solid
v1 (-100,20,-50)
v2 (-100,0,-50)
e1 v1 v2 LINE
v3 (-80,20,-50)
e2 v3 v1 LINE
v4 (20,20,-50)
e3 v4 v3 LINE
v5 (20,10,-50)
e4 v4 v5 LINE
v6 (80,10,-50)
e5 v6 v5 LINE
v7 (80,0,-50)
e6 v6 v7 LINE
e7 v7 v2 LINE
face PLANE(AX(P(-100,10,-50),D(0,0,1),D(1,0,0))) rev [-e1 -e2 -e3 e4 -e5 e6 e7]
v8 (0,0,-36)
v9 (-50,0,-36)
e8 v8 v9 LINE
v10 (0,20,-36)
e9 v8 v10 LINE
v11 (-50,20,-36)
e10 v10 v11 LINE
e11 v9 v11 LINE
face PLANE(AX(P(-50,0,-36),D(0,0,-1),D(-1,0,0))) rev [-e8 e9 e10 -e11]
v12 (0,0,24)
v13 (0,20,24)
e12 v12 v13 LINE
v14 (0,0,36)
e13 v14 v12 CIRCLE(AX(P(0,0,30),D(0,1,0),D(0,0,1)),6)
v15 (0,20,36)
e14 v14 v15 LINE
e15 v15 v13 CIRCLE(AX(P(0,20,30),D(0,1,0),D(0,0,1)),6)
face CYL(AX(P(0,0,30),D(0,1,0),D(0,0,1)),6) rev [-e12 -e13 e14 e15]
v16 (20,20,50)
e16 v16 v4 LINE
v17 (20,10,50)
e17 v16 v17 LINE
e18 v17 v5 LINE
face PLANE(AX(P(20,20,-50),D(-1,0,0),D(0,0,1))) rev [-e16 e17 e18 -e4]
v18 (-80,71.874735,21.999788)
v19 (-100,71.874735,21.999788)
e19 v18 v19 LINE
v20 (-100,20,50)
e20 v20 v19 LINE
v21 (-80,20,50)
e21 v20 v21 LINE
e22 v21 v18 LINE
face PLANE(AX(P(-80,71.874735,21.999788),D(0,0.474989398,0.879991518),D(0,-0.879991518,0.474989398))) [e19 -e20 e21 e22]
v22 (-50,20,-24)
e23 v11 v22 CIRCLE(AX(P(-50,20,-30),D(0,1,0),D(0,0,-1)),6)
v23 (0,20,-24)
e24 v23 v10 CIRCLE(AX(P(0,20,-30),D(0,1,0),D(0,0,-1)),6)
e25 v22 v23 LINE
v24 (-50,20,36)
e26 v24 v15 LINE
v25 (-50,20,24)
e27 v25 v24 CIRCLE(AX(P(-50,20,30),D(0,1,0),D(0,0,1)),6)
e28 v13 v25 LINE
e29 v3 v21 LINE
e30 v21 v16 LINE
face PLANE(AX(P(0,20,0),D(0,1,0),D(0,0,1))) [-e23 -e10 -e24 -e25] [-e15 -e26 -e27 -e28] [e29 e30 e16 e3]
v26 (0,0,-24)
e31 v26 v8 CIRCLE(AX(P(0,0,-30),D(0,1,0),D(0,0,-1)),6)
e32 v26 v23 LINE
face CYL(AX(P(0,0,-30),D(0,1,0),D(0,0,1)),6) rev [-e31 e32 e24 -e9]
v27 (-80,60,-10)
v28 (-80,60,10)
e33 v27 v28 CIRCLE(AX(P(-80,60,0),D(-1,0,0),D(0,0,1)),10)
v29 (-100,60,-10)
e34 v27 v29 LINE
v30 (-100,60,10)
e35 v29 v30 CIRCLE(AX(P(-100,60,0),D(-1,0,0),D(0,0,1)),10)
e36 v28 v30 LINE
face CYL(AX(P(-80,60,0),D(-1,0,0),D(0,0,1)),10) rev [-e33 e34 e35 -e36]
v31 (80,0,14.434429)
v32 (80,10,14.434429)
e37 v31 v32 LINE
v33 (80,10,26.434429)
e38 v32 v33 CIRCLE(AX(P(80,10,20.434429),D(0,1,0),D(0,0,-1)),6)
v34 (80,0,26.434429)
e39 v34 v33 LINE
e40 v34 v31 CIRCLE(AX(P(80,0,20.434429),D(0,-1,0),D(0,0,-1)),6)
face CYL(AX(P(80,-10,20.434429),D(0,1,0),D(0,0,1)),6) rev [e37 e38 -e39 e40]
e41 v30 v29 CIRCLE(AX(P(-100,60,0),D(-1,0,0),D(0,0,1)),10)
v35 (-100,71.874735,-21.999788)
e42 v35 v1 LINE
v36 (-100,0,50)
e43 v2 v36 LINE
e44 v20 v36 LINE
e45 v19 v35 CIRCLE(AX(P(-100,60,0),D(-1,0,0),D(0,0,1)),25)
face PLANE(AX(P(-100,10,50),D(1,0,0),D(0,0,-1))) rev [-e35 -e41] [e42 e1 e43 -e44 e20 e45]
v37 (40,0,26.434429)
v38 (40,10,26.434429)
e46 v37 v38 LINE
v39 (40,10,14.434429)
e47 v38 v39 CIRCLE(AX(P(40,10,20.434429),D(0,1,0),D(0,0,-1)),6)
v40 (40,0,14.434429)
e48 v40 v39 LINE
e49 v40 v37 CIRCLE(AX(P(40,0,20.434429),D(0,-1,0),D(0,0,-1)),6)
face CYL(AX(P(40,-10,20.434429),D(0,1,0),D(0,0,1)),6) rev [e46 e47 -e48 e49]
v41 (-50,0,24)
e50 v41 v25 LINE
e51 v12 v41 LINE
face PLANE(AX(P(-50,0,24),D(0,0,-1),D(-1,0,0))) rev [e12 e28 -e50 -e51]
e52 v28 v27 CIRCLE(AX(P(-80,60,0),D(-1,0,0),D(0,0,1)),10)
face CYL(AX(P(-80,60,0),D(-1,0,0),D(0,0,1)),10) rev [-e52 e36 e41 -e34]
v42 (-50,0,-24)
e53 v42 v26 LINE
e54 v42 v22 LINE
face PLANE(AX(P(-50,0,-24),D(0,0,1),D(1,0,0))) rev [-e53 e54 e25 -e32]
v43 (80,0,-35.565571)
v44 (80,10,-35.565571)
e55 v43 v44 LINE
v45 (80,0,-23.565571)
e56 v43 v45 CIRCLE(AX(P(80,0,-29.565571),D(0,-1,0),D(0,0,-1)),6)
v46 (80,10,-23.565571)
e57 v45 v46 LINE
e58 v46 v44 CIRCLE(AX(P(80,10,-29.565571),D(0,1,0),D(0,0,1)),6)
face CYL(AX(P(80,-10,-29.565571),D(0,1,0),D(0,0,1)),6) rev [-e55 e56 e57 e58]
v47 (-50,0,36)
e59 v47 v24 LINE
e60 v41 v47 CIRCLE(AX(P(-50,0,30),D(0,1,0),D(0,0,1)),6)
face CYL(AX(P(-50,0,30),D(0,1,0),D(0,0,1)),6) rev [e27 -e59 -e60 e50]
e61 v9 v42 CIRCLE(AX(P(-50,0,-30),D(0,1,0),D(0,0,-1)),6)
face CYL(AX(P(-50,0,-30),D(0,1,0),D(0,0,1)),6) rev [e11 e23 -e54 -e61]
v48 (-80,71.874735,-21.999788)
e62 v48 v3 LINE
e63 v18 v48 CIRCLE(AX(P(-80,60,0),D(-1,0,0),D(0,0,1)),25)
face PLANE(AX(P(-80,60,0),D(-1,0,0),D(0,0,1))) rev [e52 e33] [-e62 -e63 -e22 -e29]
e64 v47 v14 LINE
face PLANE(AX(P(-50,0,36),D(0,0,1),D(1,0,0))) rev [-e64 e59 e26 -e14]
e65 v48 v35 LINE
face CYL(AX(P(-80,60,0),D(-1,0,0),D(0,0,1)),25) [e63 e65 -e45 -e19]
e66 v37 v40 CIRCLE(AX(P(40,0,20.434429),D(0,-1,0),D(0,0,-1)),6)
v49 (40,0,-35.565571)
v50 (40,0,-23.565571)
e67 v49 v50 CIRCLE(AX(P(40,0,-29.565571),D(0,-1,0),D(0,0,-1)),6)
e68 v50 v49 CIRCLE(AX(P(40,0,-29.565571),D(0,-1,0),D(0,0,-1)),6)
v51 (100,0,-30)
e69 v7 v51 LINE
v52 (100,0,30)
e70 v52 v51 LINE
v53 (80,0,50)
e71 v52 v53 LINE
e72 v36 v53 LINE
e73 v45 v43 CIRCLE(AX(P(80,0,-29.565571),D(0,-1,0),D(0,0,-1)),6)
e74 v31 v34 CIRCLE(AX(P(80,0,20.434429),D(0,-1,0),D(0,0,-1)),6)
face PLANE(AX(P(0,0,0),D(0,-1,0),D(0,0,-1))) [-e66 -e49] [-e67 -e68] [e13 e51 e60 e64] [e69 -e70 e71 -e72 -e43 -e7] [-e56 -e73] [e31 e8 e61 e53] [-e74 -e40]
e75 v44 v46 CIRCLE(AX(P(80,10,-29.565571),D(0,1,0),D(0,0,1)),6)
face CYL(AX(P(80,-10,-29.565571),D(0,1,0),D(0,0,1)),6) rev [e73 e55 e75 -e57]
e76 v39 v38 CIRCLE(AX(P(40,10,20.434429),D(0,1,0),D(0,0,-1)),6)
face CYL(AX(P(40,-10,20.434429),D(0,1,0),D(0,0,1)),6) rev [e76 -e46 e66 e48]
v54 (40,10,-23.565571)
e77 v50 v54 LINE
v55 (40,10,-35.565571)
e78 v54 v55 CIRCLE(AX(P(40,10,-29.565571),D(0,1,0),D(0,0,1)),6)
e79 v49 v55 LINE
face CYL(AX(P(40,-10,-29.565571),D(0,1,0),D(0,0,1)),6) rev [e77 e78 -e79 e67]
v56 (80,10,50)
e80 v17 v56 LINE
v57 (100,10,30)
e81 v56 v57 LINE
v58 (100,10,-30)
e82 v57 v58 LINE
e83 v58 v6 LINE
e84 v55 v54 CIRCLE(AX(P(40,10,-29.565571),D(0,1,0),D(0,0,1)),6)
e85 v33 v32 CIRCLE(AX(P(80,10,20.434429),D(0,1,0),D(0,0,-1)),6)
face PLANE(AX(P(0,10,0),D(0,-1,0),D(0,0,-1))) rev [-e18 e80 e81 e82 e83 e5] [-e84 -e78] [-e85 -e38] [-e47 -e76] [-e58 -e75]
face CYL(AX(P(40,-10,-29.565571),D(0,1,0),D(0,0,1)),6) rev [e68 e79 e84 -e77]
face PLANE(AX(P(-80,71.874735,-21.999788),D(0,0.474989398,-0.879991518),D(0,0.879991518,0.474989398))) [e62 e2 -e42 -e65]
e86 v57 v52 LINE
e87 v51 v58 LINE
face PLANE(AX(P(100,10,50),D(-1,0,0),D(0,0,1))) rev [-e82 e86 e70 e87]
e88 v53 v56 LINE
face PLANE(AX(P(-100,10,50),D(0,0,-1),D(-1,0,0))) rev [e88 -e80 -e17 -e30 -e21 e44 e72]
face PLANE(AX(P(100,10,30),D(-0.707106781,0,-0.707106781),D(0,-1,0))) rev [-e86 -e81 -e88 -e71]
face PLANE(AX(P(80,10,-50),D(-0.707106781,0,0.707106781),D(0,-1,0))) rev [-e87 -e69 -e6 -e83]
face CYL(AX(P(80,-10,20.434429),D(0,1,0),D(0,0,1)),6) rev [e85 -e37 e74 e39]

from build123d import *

# Parameters (mm, degrees)
BASE_PLATE_SKETCH_W       = 200
BASE_PLATE_SKETCH_H       = 100
BASE_PLATE_DEPTH          = 10
RAISED_PAD_SKETCH_W       = 120
RAISED_PAD_SKETCH_H       = 100
RAISED_PAD_DEPTH          = 10
CORNER_CHAMFER_A_SIZE     = 20
CORNER_CHAMFER_B_SIZE     = 20
ADJUSTMENT_SLOTS_2X_DEPTH = 20
LUG_SKETCH_R              = 10
PIERCED_LUG_DEPTH         = 20
MOUNTING_HOLES_SKETCH_R   = 6
MOUNTING_HOLES_4X_DEPTH   = 20


with BuildPart() as part:
    # Base Plate Sketch → Base Plate (new body)
    with BuildSketch(Plane(origin=(0, 0, 0), x_dir=(1, 0, 0), z_dir=(0, 1, 0))):
        Rectangle(BASE_PLATE_SKETCH_W, BASE_PLATE_SKETCH_H)
    extrude(amount=BASE_PLATE_DEPTH)

    # Raised Pad Sketch → Raised Pad (add)
    with BuildSketch(Plane(origin=(0, 10, 0), x_dir=(1, 0, 0), z_dir=(0, 1, 0))):
        with Locations((-40, 0)):
            Rectangle(RAISED_PAD_SKETCH_W, RAISED_PAD_SKETCH_H)
    extrude(amount=RAISED_PAD_DEPTH)

    # Corner Chamfer A
    corner_chamfer_a_edges = [part.edges().sort_by_distance(p)[0] for p in [
        (100, 5, 50),
    ]]
    chamfer(corner_chamfer_a_edges, length=CORNER_CHAMFER_A_SIZE)

    # Corner Chamfer B
    corner_chamfer_b_edges = [part.edges().sort_by_distance(p)[0] for p in [
        (100, 5, -50),
    ]]
    chamfer(corner_chamfer_b_edges, length=CORNER_CHAMFER_B_SIZE)

    # Adjustment Slots Sketch → Adjustment Slots 2x (cut)
    with BuildSketch(Plane(origin=(0, 20, 0), x_dir=(1, 0, 0), z_dir=(0, 1, 0))):
        with BuildLine():
            Line((-50, -24), (0, -24))
            ThreePointArc((0, -24), (6, -30), (0, -36))
            Line((0, -36), (-50, -36))
            ThreePointArc((-50, -36), (-56, -30), (-50, -24))
        make_face()
        with BuildLine():
            Line((-50, 24), (0, 24))
            ThreePointArc((0, 24), (6, 30), (0, 36))
            Line((0, 36), (-50, 36))
            ThreePointArc((-50, 36), (-56, 30), (-50, 24))
        make_face()
    extrude(amount=-ADJUSTMENT_SLOTS_2X_DEPTH, mode=Mode.SUBTRACT)

    # Lug Sketch → Pierced Lug (add)
    with BuildSketch(Plane.ZY.offset(100)):
        with BuildLine():
            Line((-21.999787954, 71.874734943), (-50, 20))
            Line((-50, 20), (50, 20))
            Line((50, 20), (21.999787954, 71.874734943))
            ThreePointArc((21.999787954, 71.874734943), (0, 85), (-21.999787954, 71.874734943))
        make_face()
        with Locations((0, 60)):
            Circle(LUG_SKETCH_R, mode=Mode.SUBTRACT)
    extrude(amount=-PIERCED_LUG_DEPTH)

    # Mounting Holes Sketch → Mounting Holes 4x (cut)
    with BuildSketch(Plane(origin=(0, 10, 0), x_dir=(1, 0, 0), z_dir=(0, 1, 0))):
        with Locations(Location((40, 29.565570893, 0), (0, 0, 270))):
            Circle(MOUNTING_HOLES_SKETCH_R)
        with Locations(Location((80, 29.565570893, 0), (0, 0, 270))):
            Circle(MOUNTING_HOLES_SKETCH_R)
        with Locations(Location((80, -20.434429107, 0), (0, 0, 90))):
            Circle(MOUNTING_HOLES_SKETCH_R)
        with Locations(Location((40, -20.434429107, 0), (0, 0, 90))):
            Circle(MOUNTING_HOLES_SKETCH_R)
    extrude(amount=-MOUNTING_HOLES_4X_DEPTH, mode=Mode.SUBTRACT)


solid = part.part
